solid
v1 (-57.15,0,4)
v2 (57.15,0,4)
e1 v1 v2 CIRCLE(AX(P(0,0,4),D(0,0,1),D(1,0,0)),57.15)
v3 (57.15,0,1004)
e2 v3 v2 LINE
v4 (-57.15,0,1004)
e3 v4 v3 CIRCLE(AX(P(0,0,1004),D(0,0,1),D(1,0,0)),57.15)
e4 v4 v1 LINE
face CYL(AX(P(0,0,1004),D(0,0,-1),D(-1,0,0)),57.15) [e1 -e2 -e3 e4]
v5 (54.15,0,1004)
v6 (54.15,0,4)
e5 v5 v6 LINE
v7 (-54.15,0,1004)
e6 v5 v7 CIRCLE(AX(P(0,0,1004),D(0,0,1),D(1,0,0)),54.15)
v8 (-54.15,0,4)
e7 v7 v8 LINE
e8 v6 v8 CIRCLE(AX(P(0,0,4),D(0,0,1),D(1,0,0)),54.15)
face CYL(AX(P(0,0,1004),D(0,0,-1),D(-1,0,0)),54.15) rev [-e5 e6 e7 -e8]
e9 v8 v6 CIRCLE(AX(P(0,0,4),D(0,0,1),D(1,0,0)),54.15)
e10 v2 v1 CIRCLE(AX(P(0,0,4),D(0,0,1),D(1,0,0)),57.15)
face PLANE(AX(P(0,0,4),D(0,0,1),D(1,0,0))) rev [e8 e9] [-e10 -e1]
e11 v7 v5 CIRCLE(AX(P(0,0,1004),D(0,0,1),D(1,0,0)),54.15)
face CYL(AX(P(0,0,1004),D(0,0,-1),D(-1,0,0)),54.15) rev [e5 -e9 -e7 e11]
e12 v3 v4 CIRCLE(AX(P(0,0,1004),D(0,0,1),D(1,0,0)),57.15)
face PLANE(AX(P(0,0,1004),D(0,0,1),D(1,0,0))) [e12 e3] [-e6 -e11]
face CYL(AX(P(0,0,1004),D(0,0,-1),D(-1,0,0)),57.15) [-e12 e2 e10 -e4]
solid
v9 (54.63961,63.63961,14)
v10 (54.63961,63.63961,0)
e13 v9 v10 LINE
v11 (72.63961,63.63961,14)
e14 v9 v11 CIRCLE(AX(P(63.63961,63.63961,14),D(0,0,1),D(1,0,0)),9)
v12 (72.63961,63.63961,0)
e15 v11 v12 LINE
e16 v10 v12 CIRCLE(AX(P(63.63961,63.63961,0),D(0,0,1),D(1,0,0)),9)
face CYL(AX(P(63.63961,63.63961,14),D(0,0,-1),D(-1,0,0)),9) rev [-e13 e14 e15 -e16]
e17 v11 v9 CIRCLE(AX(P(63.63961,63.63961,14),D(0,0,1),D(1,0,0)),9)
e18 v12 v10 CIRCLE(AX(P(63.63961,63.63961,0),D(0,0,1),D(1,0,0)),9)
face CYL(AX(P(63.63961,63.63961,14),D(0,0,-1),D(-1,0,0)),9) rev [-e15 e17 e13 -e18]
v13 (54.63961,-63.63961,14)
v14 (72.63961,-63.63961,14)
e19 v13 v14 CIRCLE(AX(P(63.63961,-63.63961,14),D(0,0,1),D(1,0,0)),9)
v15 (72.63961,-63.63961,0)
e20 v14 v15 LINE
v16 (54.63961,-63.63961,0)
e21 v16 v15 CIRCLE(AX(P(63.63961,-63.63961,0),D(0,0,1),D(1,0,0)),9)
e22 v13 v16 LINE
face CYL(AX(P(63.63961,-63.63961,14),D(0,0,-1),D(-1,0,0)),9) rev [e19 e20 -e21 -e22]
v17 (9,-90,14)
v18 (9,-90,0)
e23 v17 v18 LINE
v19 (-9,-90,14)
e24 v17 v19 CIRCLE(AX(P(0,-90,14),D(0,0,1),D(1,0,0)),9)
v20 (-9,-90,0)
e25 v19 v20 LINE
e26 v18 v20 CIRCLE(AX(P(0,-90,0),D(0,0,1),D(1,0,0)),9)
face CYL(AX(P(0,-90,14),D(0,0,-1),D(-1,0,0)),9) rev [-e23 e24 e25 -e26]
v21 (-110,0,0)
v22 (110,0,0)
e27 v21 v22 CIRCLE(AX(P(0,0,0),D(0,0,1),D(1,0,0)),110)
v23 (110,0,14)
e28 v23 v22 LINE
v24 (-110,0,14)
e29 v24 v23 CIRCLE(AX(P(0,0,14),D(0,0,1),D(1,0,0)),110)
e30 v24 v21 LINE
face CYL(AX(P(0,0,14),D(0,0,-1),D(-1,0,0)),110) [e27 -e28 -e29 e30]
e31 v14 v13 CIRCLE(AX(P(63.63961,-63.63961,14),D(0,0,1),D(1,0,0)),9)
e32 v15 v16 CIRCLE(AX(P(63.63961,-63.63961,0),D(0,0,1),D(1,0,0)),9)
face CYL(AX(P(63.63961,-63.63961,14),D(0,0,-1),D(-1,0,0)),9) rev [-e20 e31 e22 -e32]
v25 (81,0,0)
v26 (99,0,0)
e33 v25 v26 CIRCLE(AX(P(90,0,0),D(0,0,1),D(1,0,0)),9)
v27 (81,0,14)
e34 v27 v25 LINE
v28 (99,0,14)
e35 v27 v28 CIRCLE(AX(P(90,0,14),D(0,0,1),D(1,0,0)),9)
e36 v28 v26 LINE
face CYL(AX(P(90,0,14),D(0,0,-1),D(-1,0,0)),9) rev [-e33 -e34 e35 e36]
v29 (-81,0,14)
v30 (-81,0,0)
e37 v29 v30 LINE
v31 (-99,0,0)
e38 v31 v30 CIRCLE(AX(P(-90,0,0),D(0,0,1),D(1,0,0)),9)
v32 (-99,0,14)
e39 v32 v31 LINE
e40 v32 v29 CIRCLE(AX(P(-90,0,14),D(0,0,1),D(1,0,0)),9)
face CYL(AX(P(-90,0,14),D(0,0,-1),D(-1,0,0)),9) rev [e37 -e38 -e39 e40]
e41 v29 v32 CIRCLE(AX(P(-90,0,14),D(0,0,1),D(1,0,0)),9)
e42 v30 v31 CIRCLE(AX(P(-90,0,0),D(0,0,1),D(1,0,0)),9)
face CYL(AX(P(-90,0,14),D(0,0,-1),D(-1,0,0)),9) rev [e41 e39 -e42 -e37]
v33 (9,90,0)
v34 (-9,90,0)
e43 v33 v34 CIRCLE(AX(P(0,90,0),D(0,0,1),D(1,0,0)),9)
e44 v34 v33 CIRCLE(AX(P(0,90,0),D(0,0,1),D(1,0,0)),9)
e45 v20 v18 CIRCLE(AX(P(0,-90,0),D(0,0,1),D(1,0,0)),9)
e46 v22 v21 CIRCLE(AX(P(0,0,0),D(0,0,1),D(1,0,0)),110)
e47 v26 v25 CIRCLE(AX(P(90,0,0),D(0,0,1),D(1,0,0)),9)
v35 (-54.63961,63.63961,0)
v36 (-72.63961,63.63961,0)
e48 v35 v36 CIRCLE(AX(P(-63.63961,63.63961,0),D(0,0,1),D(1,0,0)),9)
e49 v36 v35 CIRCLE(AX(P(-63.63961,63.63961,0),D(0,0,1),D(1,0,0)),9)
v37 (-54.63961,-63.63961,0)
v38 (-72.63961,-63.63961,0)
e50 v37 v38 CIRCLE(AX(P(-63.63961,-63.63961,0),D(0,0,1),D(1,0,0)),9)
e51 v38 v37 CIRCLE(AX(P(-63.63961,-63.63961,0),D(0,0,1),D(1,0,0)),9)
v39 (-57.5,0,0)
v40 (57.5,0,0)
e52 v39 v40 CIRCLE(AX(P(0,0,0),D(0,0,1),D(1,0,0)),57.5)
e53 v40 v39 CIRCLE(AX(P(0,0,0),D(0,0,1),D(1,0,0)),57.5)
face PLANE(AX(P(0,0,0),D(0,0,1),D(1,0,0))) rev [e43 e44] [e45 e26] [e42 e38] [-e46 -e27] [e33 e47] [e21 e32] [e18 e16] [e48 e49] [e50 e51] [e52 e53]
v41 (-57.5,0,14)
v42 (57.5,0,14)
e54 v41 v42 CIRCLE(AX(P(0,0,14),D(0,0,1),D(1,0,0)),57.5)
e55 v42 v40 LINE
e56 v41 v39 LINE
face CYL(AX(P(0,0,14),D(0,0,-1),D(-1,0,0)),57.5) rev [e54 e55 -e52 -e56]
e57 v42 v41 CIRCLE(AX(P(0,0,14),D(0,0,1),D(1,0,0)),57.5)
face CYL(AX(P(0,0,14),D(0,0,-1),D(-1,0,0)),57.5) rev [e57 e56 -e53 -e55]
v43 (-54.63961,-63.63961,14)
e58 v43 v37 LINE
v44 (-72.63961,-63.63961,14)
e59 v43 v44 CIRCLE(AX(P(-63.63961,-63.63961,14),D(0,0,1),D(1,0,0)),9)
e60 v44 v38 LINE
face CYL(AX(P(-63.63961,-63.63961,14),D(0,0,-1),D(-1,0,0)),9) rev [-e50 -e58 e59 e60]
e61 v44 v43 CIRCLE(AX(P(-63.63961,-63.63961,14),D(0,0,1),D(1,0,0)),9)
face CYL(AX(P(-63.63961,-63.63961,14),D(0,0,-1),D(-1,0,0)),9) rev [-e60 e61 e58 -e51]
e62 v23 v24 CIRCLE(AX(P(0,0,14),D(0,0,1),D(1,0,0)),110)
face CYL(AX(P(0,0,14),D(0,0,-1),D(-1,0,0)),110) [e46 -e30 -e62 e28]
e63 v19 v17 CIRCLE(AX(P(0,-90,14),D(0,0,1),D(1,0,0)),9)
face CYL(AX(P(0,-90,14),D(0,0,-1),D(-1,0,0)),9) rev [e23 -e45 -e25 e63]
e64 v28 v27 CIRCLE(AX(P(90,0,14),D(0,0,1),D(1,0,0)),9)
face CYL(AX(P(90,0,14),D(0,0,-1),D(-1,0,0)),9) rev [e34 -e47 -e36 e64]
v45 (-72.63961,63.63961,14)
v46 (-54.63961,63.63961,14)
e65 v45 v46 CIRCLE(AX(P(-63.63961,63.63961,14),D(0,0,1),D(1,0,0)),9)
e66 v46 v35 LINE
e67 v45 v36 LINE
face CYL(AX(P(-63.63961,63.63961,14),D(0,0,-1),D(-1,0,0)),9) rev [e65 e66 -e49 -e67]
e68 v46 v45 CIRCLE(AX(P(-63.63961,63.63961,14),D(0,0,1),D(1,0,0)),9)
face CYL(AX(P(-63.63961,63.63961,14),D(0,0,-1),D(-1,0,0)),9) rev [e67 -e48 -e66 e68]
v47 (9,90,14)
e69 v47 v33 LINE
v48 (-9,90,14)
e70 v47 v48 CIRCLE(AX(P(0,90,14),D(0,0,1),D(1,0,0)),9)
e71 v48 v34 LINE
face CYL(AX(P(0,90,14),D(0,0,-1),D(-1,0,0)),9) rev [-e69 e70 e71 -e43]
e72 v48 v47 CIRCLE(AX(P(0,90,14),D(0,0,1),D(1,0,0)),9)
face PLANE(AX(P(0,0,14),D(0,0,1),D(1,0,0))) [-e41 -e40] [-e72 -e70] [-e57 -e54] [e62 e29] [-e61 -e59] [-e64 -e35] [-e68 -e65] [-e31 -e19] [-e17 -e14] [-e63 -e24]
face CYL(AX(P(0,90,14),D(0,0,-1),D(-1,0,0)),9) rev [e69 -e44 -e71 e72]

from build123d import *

# Parameters (mm, degrees)
SKETCH1_R           = 110
SKETCH1_R_2         = 57.5
SKETCH1_R_3         = 9
BOSS_EXTRUDE1_DEPTH = 14
SKETCH2_R           = 57.15
SKETCH2_R_2         = 54.15
BOSS_EXTRUDE2_DEPTH = 1000


with BuildPart() as part:
    # Sketch1 → Boss-Extrude1 (new body)
    with BuildSketch(Plane.XY):
        Circle(SKETCH1_R)
        Circle(SKETCH1_R_2, mode=Mode.SUBTRACT)
        with Locations((0, 90)):
            Circle(SKETCH1_R_3, mode=Mode.SUBTRACT)
        with Locations((63.639610307, 63.639610307)):
            Circle(SKETCH1_R_3, mode=Mode.SUBTRACT)
        with Locations((90, 0)):
            Circle(SKETCH1_R_3, mode=Mode.SUBTRACT)
        with Locations((63.639610307, -63.639610307)):
            Circle(SKETCH1_R_3, mode=Mode.SUBTRACT)
        with Locations((0, -90)):
            Circle(SKETCH1_R_3, mode=Mode.SUBTRACT)
        with Locations((-63.639610307, -63.639610307)):
            Circle(SKETCH1_R_3, mode=Mode.SUBTRACT)
        with Locations((-90, 0)):
            Circle(SKETCH1_R_3, mode=Mode.SUBTRACT)
        with Locations((-63.639610307, 63.639610307)):
            Circle(SKETCH1_R_3, mode=Mode.SUBTRACT)
    extrude(amount=BOSS_EXTRUDE1_DEPTH)


with BuildPart() as body_2:
    # Sketch2 → Boss-Extrude2 (new body)
    with BuildSketch(Plane.XY.offset(4)):
        Circle(SKETCH2_R)
        Circle(SKETCH2_R_2, mode=Mode.SUBTRACT)
    extrude(amount=BOSS_EXTRUDE2_DEPTH)


solid = Compound([part.part, body_2.part])
